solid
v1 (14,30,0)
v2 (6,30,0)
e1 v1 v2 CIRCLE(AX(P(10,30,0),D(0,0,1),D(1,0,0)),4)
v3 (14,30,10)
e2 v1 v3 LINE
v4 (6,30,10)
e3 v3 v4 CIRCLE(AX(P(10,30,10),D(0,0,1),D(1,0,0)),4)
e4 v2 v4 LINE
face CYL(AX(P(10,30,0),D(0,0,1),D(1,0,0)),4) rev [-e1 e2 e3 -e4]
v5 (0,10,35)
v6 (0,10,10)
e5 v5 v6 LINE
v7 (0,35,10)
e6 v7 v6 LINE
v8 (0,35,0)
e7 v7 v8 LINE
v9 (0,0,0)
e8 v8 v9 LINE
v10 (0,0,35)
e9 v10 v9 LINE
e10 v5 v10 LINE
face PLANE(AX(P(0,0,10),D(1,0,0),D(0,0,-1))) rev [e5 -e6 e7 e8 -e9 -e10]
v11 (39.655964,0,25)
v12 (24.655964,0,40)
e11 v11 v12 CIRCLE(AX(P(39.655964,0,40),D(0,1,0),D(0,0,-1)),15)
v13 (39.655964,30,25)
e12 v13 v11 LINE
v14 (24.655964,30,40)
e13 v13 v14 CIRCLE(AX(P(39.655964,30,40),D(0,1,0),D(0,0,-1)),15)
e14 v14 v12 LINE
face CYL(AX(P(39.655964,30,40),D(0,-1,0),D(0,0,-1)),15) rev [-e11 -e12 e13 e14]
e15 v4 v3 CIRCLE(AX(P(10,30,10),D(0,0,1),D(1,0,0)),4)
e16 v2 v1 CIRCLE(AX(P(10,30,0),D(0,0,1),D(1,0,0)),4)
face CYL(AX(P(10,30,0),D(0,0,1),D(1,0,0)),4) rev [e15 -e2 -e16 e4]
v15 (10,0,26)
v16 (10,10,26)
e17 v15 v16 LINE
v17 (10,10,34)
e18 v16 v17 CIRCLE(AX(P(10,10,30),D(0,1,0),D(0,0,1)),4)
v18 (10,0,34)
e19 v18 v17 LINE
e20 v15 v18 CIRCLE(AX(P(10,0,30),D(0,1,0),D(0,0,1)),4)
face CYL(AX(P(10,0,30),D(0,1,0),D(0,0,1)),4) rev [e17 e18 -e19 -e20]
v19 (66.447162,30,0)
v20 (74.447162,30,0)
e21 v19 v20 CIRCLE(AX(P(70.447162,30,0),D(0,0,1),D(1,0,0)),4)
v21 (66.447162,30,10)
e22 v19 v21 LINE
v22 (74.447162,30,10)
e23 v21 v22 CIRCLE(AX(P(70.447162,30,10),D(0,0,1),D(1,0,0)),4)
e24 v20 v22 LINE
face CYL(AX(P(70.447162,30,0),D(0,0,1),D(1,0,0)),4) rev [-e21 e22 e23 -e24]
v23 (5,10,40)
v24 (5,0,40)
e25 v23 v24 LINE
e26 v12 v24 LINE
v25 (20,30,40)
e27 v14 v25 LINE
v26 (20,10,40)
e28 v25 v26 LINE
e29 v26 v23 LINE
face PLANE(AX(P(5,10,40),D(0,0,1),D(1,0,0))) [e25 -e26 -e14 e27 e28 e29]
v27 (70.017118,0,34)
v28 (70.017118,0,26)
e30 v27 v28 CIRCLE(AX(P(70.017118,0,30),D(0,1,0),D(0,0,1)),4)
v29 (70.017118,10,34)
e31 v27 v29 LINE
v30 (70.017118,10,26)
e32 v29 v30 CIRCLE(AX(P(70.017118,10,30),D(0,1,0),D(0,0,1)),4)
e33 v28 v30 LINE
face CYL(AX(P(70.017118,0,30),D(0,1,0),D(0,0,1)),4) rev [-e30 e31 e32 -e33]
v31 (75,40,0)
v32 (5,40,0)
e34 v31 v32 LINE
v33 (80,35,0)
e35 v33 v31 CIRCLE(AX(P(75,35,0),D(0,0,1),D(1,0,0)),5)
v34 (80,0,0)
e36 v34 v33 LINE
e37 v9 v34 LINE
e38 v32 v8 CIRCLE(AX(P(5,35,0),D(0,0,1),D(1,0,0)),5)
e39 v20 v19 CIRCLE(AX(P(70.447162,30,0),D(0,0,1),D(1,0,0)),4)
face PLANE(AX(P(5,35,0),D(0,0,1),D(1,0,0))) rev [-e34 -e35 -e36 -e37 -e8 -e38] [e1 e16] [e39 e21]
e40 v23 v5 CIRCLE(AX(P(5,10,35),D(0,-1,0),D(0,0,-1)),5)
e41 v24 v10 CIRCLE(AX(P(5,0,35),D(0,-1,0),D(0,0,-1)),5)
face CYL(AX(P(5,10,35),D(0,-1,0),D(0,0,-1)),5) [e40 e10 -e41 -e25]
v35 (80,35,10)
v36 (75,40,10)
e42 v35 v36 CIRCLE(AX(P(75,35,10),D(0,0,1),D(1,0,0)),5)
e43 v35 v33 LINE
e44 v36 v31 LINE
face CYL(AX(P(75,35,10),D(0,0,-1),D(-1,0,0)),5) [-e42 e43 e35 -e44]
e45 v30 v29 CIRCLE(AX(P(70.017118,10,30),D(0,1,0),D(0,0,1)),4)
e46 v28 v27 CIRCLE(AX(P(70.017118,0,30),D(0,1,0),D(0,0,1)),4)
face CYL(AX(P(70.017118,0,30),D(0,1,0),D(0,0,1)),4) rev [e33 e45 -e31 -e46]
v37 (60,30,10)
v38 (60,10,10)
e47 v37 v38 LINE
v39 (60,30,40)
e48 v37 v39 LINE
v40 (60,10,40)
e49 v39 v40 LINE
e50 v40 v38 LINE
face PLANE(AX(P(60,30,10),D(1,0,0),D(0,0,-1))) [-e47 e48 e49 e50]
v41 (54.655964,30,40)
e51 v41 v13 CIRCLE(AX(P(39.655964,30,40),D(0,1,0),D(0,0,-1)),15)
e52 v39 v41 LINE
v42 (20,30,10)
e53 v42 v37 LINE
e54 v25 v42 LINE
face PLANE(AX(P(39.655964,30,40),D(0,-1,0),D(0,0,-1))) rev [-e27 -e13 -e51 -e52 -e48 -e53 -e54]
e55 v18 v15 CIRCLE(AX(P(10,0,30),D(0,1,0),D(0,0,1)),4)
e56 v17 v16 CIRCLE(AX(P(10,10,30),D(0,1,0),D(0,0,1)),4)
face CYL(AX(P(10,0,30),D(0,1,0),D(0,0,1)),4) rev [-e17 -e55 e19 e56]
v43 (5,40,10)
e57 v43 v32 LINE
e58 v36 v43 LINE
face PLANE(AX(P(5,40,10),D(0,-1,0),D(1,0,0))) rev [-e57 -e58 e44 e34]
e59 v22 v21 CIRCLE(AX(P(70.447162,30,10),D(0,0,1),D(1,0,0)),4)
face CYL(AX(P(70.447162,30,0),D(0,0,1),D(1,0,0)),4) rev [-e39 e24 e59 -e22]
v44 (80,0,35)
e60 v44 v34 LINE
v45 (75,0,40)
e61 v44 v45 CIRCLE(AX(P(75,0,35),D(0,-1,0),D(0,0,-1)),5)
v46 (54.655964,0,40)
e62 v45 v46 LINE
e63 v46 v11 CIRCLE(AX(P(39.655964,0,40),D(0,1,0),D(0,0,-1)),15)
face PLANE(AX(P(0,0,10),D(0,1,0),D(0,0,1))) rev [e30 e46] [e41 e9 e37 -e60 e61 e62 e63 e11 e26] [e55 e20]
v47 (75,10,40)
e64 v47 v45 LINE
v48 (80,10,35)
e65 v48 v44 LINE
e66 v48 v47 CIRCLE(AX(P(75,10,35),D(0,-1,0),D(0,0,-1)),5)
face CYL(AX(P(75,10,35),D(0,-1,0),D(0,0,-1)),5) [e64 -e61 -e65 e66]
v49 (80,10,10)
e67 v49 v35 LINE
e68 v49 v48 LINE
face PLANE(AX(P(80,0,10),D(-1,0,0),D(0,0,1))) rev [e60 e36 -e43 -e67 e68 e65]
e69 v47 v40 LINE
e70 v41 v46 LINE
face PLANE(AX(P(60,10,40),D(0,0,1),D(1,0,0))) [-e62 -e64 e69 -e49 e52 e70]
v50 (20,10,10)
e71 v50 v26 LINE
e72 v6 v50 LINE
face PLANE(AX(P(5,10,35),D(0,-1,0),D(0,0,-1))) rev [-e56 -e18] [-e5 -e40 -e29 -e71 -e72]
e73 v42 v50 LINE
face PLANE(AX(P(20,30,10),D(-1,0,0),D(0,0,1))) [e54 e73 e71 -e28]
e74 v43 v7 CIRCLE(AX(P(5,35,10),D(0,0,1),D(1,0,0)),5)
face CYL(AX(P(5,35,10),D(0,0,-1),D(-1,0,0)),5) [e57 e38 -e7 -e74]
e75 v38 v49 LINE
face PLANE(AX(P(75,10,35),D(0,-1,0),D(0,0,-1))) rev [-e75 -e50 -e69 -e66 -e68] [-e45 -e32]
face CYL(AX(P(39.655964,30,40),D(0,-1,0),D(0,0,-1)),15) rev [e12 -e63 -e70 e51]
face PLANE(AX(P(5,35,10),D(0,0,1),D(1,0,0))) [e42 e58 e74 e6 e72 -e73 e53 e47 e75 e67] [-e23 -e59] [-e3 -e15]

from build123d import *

# Parameters (mm, degrees)
BACK_PLATE_DEPTH            = 10
BASE_PLATE_DEPTH            = 10
BEARING_BLOCK_DEPTH         = 30
BACK_PLATE_HOLES_SKETCH_R   = 4
BACK_PLATE_HOLES_2X_8_DEPTH = 10
BASE_PLATE_HOLES_SKETCH_R   = 4
BASE_PLATE_HOLES_2X_8_DEPTH = 10


with BuildPart() as part:
    # Back Plate Sketch → Back Plate (new body)
    with BuildSketch(Plane.XY):
        with BuildLine():
            Line((0, 0), (80, 0))
            Line((80, 0), (80, 35))
            ThreePointArc((80, 35), (78.535533906, 38.535533906), (75, 40))
            Line((75, 40), (5, 40))
            ThreePointArc((5, 40), (1.464466094, 38.535533906), (0, 35))
            Line((0, 35), (0, 0))
        make_face()
    extrude(amount=BACK_PLATE_DEPTH)

    # Base Plate Sketch → Base Plate (add)
    with BuildSketch(Plane.XZ):
        with BuildLine():
            Line((0, 10), (0, 35))
            ThreePointArc((0, 35), (1.464466094, 38.535533906), (5, 40))
            Line((5, 40), (20, 40))
            Line((20, 40), (20, 10))
            Line((20, 10), (0, 10))
        make_face()
        with BuildLine():
            Line((80, 10), (80, 35))
            ThreePointArc((80, 35), (78.535533906, 38.535533906), (75, 40))
            Line((75, 40), (60, 40))
            Line((60, 40), (60, 10))
            Line((60, 10), (80, 10))
        make_face()
    extrude(amount=-BASE_PLATE_DEPTH)

    # Bearing Block Sketch → Bearing Block (add)
    with BuildSketch(Plane.XZ):
        with BuildLine():
            Line((20, 10), (20, 40))
            Line((20, 40), (24.655964266, 40))
            ThreePointArc((24.655964266, 40), (39.655964266, 25), (54.655964266, 40))
            Line((54.655964266, 40), (60, 40))
            Line((60, 40), (60, 10))
            Line((60, 10), (20, 10))
        make_face()
    extrude(amount=-BEARING_BLOCK_DEPTH)

    # Back Plate Holes Sketch → Back Plate Holes 2xØ8 (cut)
    with BuildSketch(Plane.XY.offset(10)):
        with Locations((10, 30)):
            Circle(BACK_PLATE_HOLES_SKETCH_R)
        with Locations((70.447162461, 30)):
            Circle(BACK_PLATE_HOLES_SKETCH_R)
    extrude(amount=-BACK_PLATE_HOLES_2X_8_DEPTH, mode=Mode.SUBTRACT)

    # Base Plate Holes Sketch → Base Plate Holes 2xØ8 (cut)
    with BuildSketch(Plane(origin=(0, 10, 0), x_dir=(1, 0, 0), z_dir=(0, 1, 0))):
        with Locations(Location((10, -30, 0), (0, 0, 270))):
            Circle(BASE_PLATE_HOLES_SKETCH_R)
        with Locations(Location((70.017117794, -30, 0), (0, 0, 270))):
            Circle(BASE_PLATE_HOLES_SKETCH_R)
    extrude(amount=-BASE_PLATE_HOLES_2X_8_DEPTH, mode=Mode.SUBTRACT)


solid = part.part
